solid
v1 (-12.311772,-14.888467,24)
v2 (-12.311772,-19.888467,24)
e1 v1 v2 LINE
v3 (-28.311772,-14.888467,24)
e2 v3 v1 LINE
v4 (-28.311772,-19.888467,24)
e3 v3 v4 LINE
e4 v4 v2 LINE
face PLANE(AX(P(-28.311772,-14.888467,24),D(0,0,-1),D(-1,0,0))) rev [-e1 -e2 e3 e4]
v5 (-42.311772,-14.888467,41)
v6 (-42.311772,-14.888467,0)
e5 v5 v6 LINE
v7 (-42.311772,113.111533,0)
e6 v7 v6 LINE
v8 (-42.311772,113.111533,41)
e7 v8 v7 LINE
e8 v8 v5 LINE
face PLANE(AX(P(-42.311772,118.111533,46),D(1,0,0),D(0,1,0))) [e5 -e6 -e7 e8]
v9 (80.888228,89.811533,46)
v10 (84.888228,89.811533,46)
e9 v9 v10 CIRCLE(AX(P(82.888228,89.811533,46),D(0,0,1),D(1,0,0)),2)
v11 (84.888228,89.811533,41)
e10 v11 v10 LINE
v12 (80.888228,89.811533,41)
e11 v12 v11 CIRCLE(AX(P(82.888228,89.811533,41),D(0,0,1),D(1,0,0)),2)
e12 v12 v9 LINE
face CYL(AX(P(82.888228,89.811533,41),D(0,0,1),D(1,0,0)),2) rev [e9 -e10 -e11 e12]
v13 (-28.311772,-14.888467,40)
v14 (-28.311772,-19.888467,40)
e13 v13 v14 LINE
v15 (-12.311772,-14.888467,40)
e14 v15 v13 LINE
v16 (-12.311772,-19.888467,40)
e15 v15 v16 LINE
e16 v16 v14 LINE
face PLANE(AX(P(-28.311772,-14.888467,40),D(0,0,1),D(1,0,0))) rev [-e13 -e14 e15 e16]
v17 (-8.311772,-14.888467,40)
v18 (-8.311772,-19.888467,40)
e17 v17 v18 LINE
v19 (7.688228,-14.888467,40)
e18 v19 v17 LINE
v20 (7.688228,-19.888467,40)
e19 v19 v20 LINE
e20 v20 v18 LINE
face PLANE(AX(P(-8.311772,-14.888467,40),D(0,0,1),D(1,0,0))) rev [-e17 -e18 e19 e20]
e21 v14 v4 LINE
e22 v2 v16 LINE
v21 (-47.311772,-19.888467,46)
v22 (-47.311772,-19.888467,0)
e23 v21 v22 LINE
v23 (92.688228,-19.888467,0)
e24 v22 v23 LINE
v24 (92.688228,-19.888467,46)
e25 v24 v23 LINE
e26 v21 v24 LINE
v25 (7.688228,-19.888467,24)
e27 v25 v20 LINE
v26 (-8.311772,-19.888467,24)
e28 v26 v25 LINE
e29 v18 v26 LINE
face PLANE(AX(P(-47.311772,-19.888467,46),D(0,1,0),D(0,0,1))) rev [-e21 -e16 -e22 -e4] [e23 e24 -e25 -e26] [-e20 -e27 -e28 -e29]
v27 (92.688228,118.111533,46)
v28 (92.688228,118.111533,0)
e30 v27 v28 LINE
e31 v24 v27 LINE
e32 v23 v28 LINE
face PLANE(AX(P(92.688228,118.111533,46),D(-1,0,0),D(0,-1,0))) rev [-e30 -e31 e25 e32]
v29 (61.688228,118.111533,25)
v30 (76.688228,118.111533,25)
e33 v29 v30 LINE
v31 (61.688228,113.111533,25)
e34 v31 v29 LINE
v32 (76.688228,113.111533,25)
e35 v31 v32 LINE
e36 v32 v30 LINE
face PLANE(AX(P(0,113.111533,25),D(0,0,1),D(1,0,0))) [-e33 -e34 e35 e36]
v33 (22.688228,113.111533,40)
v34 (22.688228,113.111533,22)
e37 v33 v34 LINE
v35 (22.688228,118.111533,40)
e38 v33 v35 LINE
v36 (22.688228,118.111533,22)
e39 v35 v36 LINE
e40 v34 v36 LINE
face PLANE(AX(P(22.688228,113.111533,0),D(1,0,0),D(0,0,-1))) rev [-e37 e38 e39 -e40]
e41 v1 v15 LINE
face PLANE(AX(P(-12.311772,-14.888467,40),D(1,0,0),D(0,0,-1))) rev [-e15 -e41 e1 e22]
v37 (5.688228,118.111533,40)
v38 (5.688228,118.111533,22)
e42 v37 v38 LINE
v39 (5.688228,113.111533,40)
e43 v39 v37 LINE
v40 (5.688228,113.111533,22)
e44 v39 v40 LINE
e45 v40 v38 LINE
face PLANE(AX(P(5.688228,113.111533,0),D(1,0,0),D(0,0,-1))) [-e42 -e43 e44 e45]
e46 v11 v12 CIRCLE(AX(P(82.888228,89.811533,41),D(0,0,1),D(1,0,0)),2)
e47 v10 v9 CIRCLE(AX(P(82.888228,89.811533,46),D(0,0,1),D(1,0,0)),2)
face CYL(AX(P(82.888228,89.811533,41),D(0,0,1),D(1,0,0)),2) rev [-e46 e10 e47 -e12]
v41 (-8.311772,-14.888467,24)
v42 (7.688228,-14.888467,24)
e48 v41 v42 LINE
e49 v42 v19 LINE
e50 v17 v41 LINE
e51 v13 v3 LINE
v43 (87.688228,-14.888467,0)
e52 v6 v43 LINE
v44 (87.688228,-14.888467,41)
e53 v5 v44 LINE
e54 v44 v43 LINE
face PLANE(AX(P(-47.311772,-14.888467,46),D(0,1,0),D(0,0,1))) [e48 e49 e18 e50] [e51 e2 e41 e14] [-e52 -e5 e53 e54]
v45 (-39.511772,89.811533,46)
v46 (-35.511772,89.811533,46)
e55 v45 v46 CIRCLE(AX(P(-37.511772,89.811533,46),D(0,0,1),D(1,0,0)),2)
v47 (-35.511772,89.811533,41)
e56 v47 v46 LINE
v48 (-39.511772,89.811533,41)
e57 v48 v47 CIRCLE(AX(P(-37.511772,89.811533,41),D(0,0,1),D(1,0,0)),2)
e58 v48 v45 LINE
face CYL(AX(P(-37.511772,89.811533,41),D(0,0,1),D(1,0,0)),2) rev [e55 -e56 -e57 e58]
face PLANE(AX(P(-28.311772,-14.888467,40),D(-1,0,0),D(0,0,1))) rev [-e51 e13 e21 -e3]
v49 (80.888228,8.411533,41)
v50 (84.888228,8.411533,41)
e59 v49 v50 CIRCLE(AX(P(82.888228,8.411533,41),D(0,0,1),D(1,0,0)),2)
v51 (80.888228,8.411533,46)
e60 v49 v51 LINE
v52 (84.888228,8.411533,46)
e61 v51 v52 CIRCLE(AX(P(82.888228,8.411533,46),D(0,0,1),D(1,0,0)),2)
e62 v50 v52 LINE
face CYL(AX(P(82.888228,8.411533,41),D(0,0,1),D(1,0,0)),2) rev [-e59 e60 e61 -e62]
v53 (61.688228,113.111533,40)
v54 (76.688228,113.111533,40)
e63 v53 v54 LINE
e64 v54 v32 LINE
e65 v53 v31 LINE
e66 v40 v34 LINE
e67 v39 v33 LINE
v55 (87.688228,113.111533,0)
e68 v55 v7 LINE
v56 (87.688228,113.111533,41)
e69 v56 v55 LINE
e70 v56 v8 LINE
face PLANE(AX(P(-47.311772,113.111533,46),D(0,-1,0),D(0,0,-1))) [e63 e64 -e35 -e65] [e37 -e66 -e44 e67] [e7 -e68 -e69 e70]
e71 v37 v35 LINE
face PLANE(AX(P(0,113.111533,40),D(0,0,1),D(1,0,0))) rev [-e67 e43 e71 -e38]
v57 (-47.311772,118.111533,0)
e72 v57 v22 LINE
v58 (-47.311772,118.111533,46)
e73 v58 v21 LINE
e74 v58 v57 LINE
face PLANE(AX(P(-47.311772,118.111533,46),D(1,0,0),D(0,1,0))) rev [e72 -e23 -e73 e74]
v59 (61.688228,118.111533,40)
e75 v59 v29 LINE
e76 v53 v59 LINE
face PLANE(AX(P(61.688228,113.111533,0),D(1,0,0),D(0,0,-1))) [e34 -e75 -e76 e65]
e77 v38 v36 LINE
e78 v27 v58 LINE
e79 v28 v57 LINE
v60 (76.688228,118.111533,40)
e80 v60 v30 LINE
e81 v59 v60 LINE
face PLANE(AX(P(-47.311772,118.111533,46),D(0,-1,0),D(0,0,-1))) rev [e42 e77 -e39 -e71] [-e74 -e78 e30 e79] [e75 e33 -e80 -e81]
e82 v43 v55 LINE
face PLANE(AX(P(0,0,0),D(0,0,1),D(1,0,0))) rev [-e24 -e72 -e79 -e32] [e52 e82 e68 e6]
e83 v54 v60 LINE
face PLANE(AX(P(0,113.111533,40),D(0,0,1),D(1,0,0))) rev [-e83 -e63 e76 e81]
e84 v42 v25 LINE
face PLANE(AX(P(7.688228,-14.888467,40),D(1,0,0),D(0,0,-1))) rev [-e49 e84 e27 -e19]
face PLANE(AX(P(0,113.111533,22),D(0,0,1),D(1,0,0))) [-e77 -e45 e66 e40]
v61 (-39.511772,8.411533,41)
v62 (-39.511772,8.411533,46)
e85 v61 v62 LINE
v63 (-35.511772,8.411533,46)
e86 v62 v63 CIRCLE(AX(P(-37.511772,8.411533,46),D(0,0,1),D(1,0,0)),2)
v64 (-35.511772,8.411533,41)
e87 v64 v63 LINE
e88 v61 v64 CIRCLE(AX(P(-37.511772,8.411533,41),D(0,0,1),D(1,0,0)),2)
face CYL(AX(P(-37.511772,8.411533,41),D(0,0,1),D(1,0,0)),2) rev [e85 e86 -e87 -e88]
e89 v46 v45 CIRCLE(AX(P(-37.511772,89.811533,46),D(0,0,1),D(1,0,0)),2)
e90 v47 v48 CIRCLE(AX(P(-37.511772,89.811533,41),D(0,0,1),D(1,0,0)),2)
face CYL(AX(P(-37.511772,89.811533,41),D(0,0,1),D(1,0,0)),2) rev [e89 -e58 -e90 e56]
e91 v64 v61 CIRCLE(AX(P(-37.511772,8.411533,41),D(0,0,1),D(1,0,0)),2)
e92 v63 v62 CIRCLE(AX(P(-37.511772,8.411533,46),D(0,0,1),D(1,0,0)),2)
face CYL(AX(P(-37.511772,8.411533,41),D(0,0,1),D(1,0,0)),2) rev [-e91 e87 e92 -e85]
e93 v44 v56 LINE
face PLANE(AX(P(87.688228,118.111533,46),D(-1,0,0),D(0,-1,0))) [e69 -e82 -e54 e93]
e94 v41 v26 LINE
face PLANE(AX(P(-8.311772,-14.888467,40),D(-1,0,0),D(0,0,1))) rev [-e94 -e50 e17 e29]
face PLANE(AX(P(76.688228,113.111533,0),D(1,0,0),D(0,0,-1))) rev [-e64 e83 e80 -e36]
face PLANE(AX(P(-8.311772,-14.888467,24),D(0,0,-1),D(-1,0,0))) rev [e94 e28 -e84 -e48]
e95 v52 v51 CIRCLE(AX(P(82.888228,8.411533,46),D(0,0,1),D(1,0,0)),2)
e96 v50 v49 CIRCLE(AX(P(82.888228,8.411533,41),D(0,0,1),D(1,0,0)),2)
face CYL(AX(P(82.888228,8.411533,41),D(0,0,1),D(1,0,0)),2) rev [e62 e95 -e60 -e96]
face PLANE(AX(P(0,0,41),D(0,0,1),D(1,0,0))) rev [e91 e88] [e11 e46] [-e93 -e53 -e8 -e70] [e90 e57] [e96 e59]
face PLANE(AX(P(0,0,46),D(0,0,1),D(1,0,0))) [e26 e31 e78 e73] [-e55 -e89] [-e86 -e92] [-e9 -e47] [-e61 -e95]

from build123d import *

# Parameters (mm, degrees)
SKETCH1_W           = 140
SKETCH1_H           = 138
BOSS_EXTRUDE1_DEPTH = 46
SHELL1_T            = -5
SKETCH9_W           = 10
SKETCH9_H           = 10
CUT_EXTRUDE2_DEPTH  = 5
SKETCH10_W          = 31
SKETCH10_H          = 22
CUT_EXTRUDE3_DEPTH  = 5
SKETCH11_W          = 17
SKETCH11_H          = 18
CUT_EXTRUDE4_DEPTH  = 5
SKETCH12_W          = 32
SKETCH12_H          = 13
CUT_EXTRUDE5_DEPTH  = 5
SKETCH13_W          = 15
SKETCH13_H          = 15
CUT_EXTRUDE6_DEPTH  = 5
SKETCH19_R          = 2
CUT_EXTRUDE8_DEPTH  = 5
SKETCH21_W          = 16
SKETCH21_H          = 16
CUT_EXTRUDE11_DEPTH = 5
SKETCH23_W          = 16
SKETCH23_H          = 16
CUT_EXTRUDE12_DEPTH = 5
SKETCH24_W          = 10
SKETCH24_H          = 10
SKETCH24_W_2        = 31
SKETCH24_H_2        = 22
SKETCH24_W_3        = 32
SKETCH24_H_3        = 13
BOSS_EXTRUDE2_DEPTH = 5


with BuildPart() as part:
    # Sketch1 → Boss-Extrude1 (new body)
    with BuildSketch(Plane.XY):
        with Locations((22.688228496, 49.11153309)):
            Rectangle(SKETCH1_W, SKETCH1_H)
    extrude(amount=BOSS_EXTRUDE1_DEPTH)

    # Shell1
    shell1_openings = [part.faces().sort_by_distance(p)[0] for p in [
        (22.688228496, 49.11153309, 0),
    ]]
    offset(amount=SHELL1_T, openings=shell1_openings, kind=Kind.INTERSECTION)

    # Sketch9 → Cut-Extrude2 (cut)
    with BuildSketch(Plane(origin=(0, 118.11153309, 0), x_dir=(1, 0, 0), z_dir=(0, 1, 0))):
        with Locations((-34.311771504, -35)):
            Rectangle(SKETCH9_W, SKETCH9_H)
    extrude(amount=-CUT_EXTRUDE2_DEPTH, mode=Mode.SUBTRACT)

    # Sketch10 → Cut-Extrude3 (cut)
    with BuildSketch(Plane(origin=(0, 118.11153309, 0), x_dir=(1, 0, 0), z_dir=(0, 1, 0))):
        with Locations((-11.811771504, -29)):
            Rectangle(SKETCH10_W, SKETCH10_H)
    extrude(amount=-CUT_EXTRUDE3_DEPTH, mode=Mode.SUBTRACT)

    # Sketch11 → Cut-Extrude4 (cut)
    with BuildSketch(Plane(origin=(0, 118.11153309, 0), x_dir=(1, 0, 0), z_dir=(0, 1, 0))):
        with Locations((14.188228496, -31)):
            Rectangle(SKETCH11_W, SKETCH11_H)
    extrude(amount=-CUT_EXTRUDE4_DEPTH, mode=Mode.SUBTRACT)

    # Sketch12 → Cut-Extrude5 (cut)
    with BuildSketch(Plane(origin=(0, 118.11153309, 0), x_dir=(1, 0, 0), z_dir=(0, 1, 0))):
        with Locations((42.688228496, -33.5)):
            Rectangle(SKETCH12_W, SKETCH12_H)
    extrude(amount=-CUT_EXTRUDE5_DEPTH, mode=Mode.SUBTRACT)

    # Sketch13 → Cut-Extrude6 (cut)
    with BuildSketch(Plane(origin=(0, 118.11153309, 0), x_dir=(1, 0, 0), z_dir=(0, 1, 0))):
        with Locations((69.188228496, -32.5)):
            Rectangle(SKETCH13_W, SKETCH13_H)
    extrude(amount=-CUT_EXTRUDE6_DEPTH, mode=Mode.SUBTRACT)

    # Sketch19 → Cut-Extrude8 (cut)
    with BuildSketch(Plane.XY.offset(46)):
        with Locations((-37.511771504, 8.41153309)):
            Circle(SKETCH19_R)
        with Locations((-37.511771504, 89.81153309)):
            Circle(SKETCH19_R)
        with Locations((82.888228496, 8.41153309)):
            Circle(SKETCH19_R)
        with Locations((82.888228496, 89.81153309)):
            Circle(SKETCH19_R)
    extrude(amount=-CUT_EXTRUDE8_DEPTH, mode=Mode.SUBTRACT)

    # Sketch21 → Cut-Extrude11 (cut)
    with BuildSketch(Plane.XZ.offset(19.88846691)):
        with Locations((-20.311771504, 32)):
            Rectangle(SKETCH21_W, SKETCH21_H)
    extrude(amount=-CUT_EXTRUDE11_DEPTH, mode=Mode.SUBTRACT)

    # Sketch23 → Cut-Extrude12 (cut)
    with BuildSketch(Plane.XZ.offset(19.88846691)):
        with Locations((-0.311771504, 32)):
            Rectangle(SKETCH23_W, SKETCH23_H)
    extrude(amount=-CUT_EXTRUDE12_DEPTH, mode=Mode.SUBTRACT)

    # Sketch24 → Boss-Extrude2 (add)
    with BuildSketch(Plane(origin=(0, 118.11153309, 0), x_dir=(1, 0, 0), z_dir=(0, 1, 0))):
        with Locations((-34.311771504, -35)):
            Rectangle(SKETCH24_W, SKETCH24_H)
        with Locations((-11.811771504, -29)):
            Rectangle(SKETCH24_W_2, SKETCH24_H_2)
        with Locations((42.688228496, -33.5)):
            Rectangle(SKETCH24_W_3, SKETCH24_H_3)
    extrude(amount=-BOSS_EXTRUDE2_DEPTH)


solid = part.part
